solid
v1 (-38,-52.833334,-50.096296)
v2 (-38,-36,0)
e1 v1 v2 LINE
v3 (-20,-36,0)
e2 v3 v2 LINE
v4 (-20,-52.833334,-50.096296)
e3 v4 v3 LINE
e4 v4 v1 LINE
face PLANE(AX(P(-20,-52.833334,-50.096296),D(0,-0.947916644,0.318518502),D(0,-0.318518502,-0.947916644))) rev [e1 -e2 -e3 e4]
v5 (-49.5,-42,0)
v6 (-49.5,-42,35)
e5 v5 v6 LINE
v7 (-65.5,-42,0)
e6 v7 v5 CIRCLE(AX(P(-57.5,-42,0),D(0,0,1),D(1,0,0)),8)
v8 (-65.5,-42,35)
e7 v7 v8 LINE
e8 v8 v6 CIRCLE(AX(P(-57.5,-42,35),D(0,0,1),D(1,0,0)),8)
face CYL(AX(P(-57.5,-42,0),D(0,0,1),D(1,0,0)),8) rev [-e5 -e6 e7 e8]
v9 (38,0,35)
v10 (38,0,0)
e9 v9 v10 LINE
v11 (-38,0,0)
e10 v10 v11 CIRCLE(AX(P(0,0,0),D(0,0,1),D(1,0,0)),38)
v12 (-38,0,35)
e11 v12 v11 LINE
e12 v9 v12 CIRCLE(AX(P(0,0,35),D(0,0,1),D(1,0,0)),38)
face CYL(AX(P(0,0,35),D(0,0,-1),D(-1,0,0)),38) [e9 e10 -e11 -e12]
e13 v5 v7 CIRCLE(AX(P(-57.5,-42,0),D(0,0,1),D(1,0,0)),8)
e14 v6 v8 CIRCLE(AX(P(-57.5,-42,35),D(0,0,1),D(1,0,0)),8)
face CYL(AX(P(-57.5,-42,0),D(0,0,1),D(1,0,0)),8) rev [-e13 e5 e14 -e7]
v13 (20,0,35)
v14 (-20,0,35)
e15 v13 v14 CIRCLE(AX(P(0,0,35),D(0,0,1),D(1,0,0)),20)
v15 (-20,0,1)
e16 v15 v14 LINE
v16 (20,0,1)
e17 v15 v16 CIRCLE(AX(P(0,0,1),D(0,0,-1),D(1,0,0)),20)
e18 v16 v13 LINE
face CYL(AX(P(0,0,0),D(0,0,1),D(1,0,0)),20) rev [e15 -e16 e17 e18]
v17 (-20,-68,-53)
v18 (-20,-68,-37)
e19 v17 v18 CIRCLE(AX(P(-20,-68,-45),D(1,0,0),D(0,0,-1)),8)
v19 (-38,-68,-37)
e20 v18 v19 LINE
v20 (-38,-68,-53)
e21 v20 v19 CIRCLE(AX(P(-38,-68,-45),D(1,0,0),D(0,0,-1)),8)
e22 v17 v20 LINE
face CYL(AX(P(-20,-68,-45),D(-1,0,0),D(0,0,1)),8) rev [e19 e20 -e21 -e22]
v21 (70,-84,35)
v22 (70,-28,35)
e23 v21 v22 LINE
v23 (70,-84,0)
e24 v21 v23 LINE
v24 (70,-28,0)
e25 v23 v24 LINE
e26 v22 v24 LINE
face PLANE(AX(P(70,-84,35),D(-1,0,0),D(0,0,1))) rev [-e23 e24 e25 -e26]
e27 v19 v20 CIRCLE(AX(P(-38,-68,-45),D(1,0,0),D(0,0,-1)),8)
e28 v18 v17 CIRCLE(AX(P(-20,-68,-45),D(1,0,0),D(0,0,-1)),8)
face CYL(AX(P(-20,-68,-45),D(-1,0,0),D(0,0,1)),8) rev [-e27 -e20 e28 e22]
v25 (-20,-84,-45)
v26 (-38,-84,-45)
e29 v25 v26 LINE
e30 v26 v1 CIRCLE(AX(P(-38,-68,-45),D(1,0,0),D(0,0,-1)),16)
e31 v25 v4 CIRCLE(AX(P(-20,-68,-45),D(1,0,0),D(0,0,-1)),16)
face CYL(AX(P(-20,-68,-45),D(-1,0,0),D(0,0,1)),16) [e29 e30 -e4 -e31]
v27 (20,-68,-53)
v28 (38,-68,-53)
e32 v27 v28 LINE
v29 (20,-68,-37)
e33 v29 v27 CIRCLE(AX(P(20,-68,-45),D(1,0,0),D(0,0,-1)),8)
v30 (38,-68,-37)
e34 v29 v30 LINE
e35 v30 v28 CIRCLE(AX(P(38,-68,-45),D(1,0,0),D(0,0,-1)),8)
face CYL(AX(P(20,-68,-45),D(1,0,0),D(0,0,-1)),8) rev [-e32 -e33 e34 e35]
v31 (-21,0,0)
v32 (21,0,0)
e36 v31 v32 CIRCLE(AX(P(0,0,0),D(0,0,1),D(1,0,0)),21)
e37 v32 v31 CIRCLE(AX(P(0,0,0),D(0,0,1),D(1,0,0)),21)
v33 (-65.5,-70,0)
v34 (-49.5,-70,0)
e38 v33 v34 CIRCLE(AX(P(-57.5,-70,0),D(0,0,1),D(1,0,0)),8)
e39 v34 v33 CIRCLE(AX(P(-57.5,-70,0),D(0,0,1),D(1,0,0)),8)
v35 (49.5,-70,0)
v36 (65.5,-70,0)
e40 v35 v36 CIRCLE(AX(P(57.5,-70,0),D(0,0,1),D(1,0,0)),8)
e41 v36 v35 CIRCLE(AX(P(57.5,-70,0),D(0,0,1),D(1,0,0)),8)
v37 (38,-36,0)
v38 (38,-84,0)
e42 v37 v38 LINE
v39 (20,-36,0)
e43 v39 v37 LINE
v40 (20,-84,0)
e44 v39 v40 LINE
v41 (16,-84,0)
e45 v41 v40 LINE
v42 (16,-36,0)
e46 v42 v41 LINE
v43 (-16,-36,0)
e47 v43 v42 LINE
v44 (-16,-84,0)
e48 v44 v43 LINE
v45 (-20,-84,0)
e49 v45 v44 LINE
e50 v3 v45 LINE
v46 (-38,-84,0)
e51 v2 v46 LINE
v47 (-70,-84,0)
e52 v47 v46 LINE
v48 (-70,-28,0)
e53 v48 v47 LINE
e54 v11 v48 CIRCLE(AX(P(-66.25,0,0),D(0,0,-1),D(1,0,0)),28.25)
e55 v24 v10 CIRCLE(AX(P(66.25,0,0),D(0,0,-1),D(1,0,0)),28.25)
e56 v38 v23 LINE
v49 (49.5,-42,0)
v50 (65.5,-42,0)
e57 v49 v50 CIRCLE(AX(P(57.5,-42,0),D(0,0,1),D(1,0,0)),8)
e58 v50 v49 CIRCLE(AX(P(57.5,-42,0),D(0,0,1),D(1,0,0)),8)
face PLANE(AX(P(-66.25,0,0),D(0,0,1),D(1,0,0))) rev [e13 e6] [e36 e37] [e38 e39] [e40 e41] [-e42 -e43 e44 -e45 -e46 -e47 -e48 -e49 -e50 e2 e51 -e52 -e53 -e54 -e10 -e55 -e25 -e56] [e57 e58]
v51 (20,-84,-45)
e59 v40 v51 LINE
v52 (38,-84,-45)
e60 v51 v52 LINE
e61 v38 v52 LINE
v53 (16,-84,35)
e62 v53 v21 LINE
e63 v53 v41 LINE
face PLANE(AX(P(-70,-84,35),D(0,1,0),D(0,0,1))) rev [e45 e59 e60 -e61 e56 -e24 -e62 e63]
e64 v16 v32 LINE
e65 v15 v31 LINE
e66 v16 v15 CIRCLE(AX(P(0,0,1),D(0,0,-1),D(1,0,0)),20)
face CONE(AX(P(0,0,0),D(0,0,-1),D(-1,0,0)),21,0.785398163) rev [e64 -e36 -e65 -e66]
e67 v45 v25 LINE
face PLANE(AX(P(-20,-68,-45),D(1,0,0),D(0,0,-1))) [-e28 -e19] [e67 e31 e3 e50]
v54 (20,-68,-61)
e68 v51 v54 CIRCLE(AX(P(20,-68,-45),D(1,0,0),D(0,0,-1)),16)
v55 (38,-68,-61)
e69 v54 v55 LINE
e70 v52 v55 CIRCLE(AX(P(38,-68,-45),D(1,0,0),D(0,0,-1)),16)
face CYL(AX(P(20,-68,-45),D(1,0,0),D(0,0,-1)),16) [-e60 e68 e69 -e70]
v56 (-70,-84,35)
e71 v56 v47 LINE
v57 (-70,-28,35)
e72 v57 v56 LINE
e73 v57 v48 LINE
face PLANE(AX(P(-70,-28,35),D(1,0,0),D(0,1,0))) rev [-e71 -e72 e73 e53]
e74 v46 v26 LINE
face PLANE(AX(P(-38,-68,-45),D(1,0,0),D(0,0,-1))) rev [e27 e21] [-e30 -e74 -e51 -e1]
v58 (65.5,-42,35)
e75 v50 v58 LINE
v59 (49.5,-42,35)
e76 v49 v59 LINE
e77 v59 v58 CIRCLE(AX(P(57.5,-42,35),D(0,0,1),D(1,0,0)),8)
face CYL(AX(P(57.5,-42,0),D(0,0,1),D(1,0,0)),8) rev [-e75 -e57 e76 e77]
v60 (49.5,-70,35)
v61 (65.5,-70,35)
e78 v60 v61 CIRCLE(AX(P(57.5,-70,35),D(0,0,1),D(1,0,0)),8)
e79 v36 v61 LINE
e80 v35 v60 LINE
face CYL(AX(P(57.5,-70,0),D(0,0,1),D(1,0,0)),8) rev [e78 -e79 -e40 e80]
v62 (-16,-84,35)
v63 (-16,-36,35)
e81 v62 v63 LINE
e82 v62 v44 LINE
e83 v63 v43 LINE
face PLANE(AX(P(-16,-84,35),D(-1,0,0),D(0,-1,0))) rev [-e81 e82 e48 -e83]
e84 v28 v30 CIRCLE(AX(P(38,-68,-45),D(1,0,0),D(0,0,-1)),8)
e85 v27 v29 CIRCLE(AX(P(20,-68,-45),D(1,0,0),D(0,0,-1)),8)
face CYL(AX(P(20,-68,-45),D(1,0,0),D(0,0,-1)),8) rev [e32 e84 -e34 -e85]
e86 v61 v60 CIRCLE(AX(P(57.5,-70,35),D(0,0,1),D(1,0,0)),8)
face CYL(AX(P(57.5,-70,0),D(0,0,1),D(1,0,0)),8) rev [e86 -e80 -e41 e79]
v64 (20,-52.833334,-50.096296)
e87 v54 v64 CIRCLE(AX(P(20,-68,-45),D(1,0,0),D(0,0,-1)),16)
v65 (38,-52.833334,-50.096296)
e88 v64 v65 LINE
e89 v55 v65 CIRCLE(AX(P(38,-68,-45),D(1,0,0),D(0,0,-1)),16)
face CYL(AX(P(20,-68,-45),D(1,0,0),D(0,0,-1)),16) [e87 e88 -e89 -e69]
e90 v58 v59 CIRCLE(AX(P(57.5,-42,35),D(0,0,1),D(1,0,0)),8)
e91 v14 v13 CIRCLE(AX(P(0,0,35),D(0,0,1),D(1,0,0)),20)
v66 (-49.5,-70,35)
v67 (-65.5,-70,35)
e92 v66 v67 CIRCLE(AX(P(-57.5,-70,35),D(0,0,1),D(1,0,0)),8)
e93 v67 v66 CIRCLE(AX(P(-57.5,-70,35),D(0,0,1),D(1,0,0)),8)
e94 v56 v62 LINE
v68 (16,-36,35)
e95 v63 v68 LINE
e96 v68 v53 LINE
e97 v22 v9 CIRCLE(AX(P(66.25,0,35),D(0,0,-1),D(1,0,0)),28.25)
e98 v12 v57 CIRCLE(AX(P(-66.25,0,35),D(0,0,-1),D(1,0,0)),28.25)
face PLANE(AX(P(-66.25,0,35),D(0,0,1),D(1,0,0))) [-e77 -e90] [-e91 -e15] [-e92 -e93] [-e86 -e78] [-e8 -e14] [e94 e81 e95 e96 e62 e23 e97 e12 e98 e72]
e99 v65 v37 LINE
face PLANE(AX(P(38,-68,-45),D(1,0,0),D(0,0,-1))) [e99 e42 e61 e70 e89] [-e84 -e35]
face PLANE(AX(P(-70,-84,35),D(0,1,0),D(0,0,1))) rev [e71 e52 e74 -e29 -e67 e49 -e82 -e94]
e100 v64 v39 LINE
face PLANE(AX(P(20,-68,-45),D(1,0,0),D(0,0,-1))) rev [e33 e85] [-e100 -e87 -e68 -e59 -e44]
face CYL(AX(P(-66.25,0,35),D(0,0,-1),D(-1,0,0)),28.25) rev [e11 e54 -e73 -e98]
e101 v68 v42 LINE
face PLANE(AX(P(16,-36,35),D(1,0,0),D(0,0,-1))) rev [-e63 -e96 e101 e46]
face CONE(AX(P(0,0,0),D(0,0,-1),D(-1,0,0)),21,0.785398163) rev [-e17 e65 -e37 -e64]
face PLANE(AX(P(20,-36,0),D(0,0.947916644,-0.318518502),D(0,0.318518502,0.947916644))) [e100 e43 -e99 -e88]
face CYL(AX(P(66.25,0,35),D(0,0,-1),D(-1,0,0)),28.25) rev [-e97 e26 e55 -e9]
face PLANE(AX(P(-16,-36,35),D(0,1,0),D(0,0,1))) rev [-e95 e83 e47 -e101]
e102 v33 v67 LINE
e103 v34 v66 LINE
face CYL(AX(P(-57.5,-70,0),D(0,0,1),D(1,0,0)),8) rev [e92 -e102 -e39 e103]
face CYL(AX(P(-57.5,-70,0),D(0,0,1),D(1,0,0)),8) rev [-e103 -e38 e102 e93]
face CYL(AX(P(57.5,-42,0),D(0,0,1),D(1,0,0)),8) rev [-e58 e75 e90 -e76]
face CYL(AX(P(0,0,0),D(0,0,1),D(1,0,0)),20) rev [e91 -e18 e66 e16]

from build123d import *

# Parameters (mm, degrees)
BASE_BLOCK_DEPTH         = 35
BORE_PROFILE_R           = 20
BORE_40_DEPTH            = 35
MOUNTING_HOLES_PROFILE_R = 8
MOUNTING_HOLES_4X_DEPTH  = 35
SIDE_ARM_PROFILE_R       = 8
SIDE_ARM_DEPTH           = 18
LUG_START                = 18
LUG_BOSS_PROFILE_R       = 8
LUG_BOSS_DEPTH           = 18
RELIEF_CUT_PROFILE_W     = 32
RELIEF_CUT_PROFILE_H     = 48
RELIEF_CUT_DEPTH         = 35
BORE_CHAMFER_1MM_SIZE    = 1


with BuildPart() as part:
    # Base Block Profile → Base Block (new body)
    with BuildSketch(Plane.XY):
        with BuildLine():
            Line((-70, -28), (-70, -84))
            Line((-70, -84), (70, -84))
            Line((70, -84), (70, -28))
            ThreePointArc((70, -28), (47.647244828, -21.260291625), (38, 0))
            ThreePointArc((38, 0), (0, 38), (-38, 0))
            ThreePointArc((-38, 0), (-47.647244828, -21.260291625), (-70, -28))
        make_face()
    extrude(amount=BASE_BLOCK_DEPTH)

    # Bore Profile → Bore Ø40 (cut)
    with BuildSketch(Plane.XY.offset(35)):
        Circle(BORE_PROFILE_R)
    extrude(amount=-BORE_40_DEPTH, mode=Mode.SUBTRACT)

    # Mounting Holes Profile → Mounting Holes 4x (cut)
    with BuildSketch(Plane.XY.offset(35)):
        with Locations((-57.5, -42)):
            Circle(MOUNTING_HOLES_PROFILE_R)
        with Locations((-57.5, -70)):
            Circle(MOUNTING_HOLES_PROFILE_R)
        with Locations((57.5, -42)):
            Circle(MOUNTING_HOLES_PROFILE_R)
        with Locations((57.5, -70)):
            Circle(MOUNTING_HOLES_PROFILE_R)
    extrude(amount=-MOUNTING_HOLES_4X_DEPTH, mode=Mode.SUBTRACT)

    # Side Arm Profile → Side Arm (add)
    with BuildSketch(Plane(origin=(38, 0, 0), x_dir=(0, 0, -1), z_dir=(1, 0, 0))):
        with BuildLine():
            Line((0, -84), (0, -36))
            Line((0, -36), (50.096296037, -52.833333698))
            ThreePointArc((50.096296037, -52.833333698), (60.790292284, -70.581989463), (45, -84))
            Line((45, -84), (0, -84))
        make_face()
        with Locations((45, -68)):
            Circle(SIDE_ARM_PROFILE_R, mode=Mode.SUBTRACT)
    extrude(amount=-SIDE_ARM_DEPTH)

    # Lug Boss Profile → Lug Boss (add)
    with BuildSketch(Plane(origin=(-38, 0, 0), x_dir=(0, 0, -1), z_dir=(1, 0, 0)).offset(LUG_START)):
        with BuildLine():
            Line((0, -36), (0, -84))
            Line((0, -84), (45, -84))
            ThreePointArc((45, -84), (60.790292284, -70.581989463), (50.096296037, -52.833333698))
            Line((50.096296037, -52.833333698), (0, -36))
        make_face()
        with Locations((45, -68)):
            Circle(LUG_BOSS_PROFILE_R, mode=Mode.SUBTRACT)
    extrude(amount=-LUG_BOSS_DEPTH)

    # Relief Cut Profile → Relief Cut (cut)
    with BuildSketch(Plane(origin=(0, 0, 0), x_dir=(-1, 0, 0), z_dir=(0, 0, -1))):
        with Locations((0, -60)):
            Rectangle(RELIEF_CUT_PROFILE_W, RELIEF_CUT_PROFILE_H)
    extrude(amount=-RELIEF_CUT_DEPTH, mode=Mode.SUBTRACT)

    # Bore Chamfer 1mm
    bore_chamfer_1mm_edges = [part.edges().sort_by_distance(p)[0] for p in [
        (-20, 0, 0),
    ]]
    chamfer(bore_chamfer_1mm_edges, length=BORE_CHAMFER_1MM_SIZE)


solid = part.part
